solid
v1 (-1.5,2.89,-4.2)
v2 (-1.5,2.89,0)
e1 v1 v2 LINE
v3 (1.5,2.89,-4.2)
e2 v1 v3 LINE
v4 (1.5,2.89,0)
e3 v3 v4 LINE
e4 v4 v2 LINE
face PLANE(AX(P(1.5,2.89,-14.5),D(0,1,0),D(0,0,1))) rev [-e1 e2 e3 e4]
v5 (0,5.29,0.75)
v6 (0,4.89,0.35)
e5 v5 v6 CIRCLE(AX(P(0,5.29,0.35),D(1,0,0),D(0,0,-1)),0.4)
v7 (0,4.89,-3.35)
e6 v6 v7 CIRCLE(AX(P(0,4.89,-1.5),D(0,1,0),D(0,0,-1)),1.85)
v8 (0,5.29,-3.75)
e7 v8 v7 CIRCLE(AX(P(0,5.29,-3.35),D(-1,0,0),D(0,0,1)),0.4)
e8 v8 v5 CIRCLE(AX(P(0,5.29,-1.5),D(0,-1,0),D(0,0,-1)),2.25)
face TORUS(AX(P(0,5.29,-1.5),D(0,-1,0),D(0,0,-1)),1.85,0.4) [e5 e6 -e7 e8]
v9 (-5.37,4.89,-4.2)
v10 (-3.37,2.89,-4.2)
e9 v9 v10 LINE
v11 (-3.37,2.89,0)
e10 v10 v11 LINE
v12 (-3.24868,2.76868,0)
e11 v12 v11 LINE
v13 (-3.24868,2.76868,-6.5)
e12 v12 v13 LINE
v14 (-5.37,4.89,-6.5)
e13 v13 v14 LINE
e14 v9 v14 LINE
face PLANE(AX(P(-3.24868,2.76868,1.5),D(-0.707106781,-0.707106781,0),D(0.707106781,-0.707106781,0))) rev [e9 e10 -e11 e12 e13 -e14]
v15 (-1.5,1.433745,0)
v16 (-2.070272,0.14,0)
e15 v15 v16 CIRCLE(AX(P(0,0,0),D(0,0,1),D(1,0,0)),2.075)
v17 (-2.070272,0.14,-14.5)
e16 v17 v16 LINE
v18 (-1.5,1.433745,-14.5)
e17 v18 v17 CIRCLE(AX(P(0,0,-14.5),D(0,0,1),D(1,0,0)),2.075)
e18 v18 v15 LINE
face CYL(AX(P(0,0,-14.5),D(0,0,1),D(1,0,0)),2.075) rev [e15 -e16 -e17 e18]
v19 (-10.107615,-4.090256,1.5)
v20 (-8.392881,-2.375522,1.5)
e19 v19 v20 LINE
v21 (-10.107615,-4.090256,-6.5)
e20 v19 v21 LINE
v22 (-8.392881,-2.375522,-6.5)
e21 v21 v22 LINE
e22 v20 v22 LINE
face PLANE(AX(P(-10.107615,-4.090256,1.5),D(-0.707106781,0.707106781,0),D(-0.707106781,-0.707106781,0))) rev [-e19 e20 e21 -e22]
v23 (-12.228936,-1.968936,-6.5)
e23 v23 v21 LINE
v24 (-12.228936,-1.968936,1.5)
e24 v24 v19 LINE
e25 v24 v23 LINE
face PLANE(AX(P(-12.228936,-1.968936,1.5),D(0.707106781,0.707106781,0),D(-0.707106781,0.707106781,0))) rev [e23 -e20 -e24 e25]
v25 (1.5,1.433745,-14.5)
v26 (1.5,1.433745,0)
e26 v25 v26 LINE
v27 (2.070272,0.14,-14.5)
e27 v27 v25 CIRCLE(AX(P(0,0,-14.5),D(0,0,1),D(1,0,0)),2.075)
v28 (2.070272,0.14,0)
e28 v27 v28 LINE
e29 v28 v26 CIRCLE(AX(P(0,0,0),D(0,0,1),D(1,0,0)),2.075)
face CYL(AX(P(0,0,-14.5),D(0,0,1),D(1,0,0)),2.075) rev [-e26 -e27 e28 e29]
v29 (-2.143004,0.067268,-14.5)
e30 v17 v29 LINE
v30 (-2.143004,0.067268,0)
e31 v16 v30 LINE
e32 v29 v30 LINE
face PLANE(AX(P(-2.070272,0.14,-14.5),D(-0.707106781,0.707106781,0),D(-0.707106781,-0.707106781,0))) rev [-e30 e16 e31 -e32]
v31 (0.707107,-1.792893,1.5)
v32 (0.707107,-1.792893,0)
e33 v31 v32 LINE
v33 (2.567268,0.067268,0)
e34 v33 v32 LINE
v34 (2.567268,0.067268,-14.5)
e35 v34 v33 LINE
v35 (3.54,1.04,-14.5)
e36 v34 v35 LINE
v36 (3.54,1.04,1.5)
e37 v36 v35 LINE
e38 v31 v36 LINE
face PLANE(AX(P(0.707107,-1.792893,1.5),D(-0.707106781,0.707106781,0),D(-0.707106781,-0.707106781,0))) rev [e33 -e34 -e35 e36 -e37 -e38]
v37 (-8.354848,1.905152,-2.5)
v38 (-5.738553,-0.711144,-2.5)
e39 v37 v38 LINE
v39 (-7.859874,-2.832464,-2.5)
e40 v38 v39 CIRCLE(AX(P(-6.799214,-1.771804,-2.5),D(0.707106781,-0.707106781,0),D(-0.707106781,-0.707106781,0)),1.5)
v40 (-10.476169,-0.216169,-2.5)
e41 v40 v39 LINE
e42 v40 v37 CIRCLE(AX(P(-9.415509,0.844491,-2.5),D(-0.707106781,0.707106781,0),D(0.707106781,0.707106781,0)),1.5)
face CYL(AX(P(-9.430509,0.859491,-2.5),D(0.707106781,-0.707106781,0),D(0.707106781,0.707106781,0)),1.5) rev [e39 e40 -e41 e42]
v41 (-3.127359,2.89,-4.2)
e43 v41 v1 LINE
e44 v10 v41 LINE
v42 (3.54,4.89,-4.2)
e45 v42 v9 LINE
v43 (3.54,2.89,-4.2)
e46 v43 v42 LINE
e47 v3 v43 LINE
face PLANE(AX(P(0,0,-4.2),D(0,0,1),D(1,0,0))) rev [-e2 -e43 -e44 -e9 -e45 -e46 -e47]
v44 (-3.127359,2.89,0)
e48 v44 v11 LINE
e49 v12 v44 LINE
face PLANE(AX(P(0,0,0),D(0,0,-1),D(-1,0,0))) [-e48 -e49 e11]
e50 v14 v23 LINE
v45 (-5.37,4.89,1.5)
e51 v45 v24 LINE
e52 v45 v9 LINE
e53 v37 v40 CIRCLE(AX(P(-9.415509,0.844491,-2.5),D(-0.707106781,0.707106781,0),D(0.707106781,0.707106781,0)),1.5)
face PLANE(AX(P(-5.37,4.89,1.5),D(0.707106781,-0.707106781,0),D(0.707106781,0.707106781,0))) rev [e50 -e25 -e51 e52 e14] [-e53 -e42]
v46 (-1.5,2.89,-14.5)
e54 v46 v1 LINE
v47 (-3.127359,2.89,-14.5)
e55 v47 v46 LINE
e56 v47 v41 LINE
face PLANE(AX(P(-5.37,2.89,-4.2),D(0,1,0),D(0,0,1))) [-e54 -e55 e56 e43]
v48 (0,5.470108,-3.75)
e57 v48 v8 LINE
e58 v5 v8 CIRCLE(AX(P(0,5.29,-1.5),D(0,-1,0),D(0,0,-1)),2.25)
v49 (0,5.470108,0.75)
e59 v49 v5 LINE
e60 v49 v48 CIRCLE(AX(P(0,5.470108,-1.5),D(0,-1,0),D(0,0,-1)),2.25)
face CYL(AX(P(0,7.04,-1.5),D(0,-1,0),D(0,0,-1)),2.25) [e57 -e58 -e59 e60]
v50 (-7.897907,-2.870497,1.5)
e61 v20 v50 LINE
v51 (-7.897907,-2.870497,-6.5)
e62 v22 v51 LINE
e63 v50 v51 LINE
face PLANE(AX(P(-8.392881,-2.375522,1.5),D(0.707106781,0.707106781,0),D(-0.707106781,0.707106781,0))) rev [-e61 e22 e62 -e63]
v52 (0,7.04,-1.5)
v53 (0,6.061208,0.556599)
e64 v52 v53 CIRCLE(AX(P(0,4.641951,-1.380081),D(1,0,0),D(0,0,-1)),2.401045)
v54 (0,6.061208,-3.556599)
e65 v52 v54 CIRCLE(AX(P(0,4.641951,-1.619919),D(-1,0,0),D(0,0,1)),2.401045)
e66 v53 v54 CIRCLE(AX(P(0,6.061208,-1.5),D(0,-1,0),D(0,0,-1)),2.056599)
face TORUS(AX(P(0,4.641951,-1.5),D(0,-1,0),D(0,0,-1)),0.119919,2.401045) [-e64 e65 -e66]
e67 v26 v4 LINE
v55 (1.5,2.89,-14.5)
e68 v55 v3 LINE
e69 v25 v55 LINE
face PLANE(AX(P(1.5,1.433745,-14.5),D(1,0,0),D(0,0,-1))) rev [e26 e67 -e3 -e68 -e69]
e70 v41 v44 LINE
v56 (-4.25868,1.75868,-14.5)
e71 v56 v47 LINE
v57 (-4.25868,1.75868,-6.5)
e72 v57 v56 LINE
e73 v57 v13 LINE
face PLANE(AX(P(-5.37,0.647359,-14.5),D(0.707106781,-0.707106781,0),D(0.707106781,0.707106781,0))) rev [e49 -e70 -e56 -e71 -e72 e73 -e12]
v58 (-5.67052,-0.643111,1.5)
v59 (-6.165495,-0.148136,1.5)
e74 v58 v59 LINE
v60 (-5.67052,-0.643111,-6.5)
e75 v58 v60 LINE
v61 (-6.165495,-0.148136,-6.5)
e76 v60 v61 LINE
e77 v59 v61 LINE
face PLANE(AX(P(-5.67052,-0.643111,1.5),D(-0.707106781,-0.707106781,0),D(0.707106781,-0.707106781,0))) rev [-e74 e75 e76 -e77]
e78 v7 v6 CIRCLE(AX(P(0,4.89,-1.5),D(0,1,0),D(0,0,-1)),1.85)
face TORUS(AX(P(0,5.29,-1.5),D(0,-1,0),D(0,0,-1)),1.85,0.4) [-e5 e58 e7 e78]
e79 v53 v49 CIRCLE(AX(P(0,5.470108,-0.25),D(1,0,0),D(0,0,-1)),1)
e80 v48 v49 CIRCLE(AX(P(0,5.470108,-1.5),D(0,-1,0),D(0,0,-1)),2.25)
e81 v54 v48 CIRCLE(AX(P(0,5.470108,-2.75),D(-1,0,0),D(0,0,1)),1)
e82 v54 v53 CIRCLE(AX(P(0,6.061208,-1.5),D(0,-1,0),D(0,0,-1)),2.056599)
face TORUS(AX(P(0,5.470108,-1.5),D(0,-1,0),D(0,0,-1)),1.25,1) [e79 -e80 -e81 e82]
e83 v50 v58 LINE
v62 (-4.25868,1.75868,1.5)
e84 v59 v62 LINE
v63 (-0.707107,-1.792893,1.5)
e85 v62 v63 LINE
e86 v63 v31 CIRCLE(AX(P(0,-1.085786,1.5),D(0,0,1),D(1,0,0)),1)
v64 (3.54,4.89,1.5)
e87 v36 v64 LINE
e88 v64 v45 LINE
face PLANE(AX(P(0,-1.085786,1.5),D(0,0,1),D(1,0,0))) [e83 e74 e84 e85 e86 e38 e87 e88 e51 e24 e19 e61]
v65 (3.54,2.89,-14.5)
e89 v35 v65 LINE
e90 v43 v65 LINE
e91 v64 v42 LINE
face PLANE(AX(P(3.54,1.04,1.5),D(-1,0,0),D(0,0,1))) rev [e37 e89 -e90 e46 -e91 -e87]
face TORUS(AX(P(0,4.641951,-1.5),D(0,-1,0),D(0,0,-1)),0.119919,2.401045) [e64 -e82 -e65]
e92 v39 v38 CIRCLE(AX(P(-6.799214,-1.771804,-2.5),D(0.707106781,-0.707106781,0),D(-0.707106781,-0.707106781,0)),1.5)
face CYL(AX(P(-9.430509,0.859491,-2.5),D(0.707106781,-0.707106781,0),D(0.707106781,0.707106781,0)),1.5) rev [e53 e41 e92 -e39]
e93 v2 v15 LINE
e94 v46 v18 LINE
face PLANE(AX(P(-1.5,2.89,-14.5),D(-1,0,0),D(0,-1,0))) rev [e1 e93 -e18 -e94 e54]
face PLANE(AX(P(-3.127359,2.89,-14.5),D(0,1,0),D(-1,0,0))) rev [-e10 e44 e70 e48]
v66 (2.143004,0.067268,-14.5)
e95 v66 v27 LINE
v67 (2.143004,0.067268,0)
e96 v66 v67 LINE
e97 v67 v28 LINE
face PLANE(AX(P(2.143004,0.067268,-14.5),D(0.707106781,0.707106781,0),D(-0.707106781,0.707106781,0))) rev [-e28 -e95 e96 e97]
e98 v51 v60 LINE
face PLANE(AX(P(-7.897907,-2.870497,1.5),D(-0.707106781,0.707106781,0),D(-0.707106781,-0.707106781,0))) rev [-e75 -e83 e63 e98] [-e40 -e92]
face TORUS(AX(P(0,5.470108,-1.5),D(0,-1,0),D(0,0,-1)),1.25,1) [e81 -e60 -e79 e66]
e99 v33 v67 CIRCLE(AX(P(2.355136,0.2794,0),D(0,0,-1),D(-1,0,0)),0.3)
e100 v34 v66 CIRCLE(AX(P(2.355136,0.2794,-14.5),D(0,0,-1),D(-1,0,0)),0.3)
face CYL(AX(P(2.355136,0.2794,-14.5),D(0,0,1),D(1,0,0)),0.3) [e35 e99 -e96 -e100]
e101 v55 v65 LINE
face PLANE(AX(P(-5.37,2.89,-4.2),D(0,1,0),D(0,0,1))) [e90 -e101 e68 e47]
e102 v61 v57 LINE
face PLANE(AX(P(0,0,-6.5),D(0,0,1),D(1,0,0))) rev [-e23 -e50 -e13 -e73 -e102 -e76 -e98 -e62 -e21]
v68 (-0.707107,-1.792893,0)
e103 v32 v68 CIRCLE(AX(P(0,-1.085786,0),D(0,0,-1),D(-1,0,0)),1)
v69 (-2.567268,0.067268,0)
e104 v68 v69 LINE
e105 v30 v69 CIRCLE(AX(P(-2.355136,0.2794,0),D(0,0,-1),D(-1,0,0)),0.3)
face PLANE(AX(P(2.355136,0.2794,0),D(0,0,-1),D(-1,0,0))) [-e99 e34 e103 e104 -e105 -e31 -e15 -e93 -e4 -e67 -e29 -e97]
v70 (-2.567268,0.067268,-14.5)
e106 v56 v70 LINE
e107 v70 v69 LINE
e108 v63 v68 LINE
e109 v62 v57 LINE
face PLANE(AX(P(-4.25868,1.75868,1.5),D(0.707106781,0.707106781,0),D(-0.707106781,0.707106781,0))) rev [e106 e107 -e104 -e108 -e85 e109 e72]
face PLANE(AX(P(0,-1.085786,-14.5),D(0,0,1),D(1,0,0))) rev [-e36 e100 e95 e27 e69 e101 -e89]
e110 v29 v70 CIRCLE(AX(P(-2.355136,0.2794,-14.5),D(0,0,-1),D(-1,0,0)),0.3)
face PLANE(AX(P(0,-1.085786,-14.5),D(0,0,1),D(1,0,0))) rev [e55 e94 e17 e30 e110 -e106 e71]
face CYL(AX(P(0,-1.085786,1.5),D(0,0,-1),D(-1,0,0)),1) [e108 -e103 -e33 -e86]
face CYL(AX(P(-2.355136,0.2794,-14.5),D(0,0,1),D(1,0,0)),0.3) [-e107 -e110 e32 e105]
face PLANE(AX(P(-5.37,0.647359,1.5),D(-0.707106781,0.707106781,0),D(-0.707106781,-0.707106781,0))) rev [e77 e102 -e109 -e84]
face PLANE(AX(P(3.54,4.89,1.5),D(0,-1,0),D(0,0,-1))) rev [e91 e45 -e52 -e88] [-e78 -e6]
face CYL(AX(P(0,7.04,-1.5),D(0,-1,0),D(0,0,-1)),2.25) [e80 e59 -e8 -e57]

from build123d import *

# Parameters (mm, degrees)
BOSS_EXTRUDE1_DEPTH = 16
SKETCH2_W           = 8.91
SKETCH2_H           = 2
CUT_EXTRUDE1_DEPTH  = 10.3
CUT_EXTRUDE2_DEPTH  = 14.5
CUT_EXTRUDE3_DEPTH  = 14.5
BOSS_EXTRUDE2_DEPTH = 8


with BuildPart() as part:
    # Sketch1 → Boss-Extrude1 (new body)
    with BuildSketch(Plane.XY.offset(-14.5)):
        with BuildLine():
            Line((-5.37, 4.89), (-5.37, 0.647359313))
            Line((-5.37, 0.647359313), (-4.258679656, 1.758679656))
            Line((-4.258679656, 1.758679656), (-0.707106781, -1.792893219))
            ThreePointArc((-0.707106781, -1.792893219), (0, -2.085786438), (0.707106781, -1.792893219))
            Line((0.707106781, -1.792893219), (3.54, 1.04))
            Line((3.54, 1.04), (3.54, 4.89))
            Line((3.54, 4.89), (-5.37, 4.89))
        make_face()
    extrude(amount=BOSS_EXTRUDE1_DEPTH)

    # Sketch2 → Cut-Extrude1 (cut)
    with BuildSketch(Plane.XY.offset(-14.5)):
        with Locations((-0.915, 3.89)):
            Rectangle(SKETCH2_W, SKETCH2_H)
    extrude(amount=CUT_EXTRUDE1_DEPTH, mode=Mode.SUBTRACT)

    # Sketch3 → Cut-Extrude2 (cut)
    with BuildSketch(Plane.XY):
        with BuildLine():
            Line((-2.64, 0.14), (-2.64, -5))
            Line((-2.64, -5), (2.64, -5))
            Line((2.64, -5), (2.64, 0.14))
            Line((2.64, 0.14), (2.567267895, 0.067267895))
            ThreePointArc((2.567267895, 0.067267895), (2.355135861, -0.020600071), (2.143003826, 0.067267895))
            Line((2.143003826, 0.067267895), (2.070271721, 0.14))
            ThreePointArc((2.070271721, 0.14), (1.898724344, 0.836941375), (1.5, 1.433745096))
            Line((1.5, 1.433745096), (1.5, 2.89))
            Line((1.5, 2.89), (-1.5, 2.89))
            Line((-1.5, 2.89), (-1.5, 1.433745096))
            ThreePointArc((-1.5, 1.433745096), (-1.898724344, 0.836941375), (-2.070271721, 0.14))
            Line((-2.070271721, 0.14), (-2.143003826, 0.067267895))
            ThreePointArc((-2.143003826, 0.067267895), (-2.355135861, -0.020600071), (-2.567267895, 0.067267895))
            Line((-2.567267895, 0.067267895), (-2.64, 0.14))
        make_face()
    extrude(amount=-CUT_EXTRUDE2_DEPTH, mode=Mode.SUBTRACT)

    # Sketch4 → Cut-Extrude3 (cut)
    with BuildSketch(Plane.XY):
        Polygon((-5.37, 0.647359313), (-3.127359313, 2.89), (-5.37, 2.89), align=None)
    extrude(amount=-CUT_EXTRUDE3_DEPTH, mode=Mode.SUBTRACT)

    # Sketch5 → Boss-Extrude2 (add)
    with BuildSketch(Plane.XY.offset(-6.5)):
        Polygon((-12.228935778, -1.968935778), (-10.107615434, -4.090256121), (-8.39288149, -2.375522177), (-7.897906743, -2.870496924), (-5.670520382, -0.643110563), (-6.165495129, -0.148135816), (-3.248679656, 2.768679656), (-5.37, 4.89), align=None)
    extrude(amount=BOSS_EXTRUDE2_DEPTH)

    # Sketch6 → Cut-Revolve1 (revolve, cut)
    with BuildSketch(Plane.XY.offset(-2.5), mode=Mode.PRIVATE) as cut_revolve1_sk:
        Polygon((-5.894974747, -2.676042559), (-6.955634919, -3.73670273), (-10.491168825, -0.201168825), (-9.430508653, 0.859491347), align=None)
    revolve(cut_revolve1_sk.sketch.rotate(Axis((-9.430508653, 0.859491347, -2.5), (0.7071067811865479, -0.7071067811865472, 0)), 180), axis=Axis((-9.430508653, 0.859491347, -2.5), (0.7071067811865479, -0.7071067811865472, 0)), mode=Mode.SUBTRACT)

    # Sketch7 → Revolve1 (revolve)
    with BuildSketch(Plane(origin=(0, 0, 0), x_dir=(0, 0, -1), z_dir=(1, 0, 0)), mode=Mode.PRIVATE) as revolve1_sk:
        with BuildLine():
            Line((1.5, 4.69), (-0.7, 4.69))
            Line((-0.7, 4.69), (-0.7, 4.89))
            Line((-0.7, 4.89), (-0.35, 4.89))
            ThreePointArc((-0.35, 4.89), (-0.632842712, 5.007157288), (-0.75, 5.29))
            Line((-0.75, 5.29), (-0.75, 5.470108292))
            ThreePointArc((-0.75, 5.470108292), (-0.700420617, 5.781075575), (-0.556598698, 6.061207725))
            ThreePointArc((-0.556598698, 6.061207725), (0.348255742, 6.809981308), (1.5, 7.04))
            Line((1.5, 7.04), (1.5, 4.69))
        make_face()
    revolve(revolve1_sk.sketch.rotate(Axis((0, 7.04, -1.5), (0, -1, 0)), 180), axis=Axis((0, 7.04, -1.5), (0, -1, 0)))


solid = part.part
